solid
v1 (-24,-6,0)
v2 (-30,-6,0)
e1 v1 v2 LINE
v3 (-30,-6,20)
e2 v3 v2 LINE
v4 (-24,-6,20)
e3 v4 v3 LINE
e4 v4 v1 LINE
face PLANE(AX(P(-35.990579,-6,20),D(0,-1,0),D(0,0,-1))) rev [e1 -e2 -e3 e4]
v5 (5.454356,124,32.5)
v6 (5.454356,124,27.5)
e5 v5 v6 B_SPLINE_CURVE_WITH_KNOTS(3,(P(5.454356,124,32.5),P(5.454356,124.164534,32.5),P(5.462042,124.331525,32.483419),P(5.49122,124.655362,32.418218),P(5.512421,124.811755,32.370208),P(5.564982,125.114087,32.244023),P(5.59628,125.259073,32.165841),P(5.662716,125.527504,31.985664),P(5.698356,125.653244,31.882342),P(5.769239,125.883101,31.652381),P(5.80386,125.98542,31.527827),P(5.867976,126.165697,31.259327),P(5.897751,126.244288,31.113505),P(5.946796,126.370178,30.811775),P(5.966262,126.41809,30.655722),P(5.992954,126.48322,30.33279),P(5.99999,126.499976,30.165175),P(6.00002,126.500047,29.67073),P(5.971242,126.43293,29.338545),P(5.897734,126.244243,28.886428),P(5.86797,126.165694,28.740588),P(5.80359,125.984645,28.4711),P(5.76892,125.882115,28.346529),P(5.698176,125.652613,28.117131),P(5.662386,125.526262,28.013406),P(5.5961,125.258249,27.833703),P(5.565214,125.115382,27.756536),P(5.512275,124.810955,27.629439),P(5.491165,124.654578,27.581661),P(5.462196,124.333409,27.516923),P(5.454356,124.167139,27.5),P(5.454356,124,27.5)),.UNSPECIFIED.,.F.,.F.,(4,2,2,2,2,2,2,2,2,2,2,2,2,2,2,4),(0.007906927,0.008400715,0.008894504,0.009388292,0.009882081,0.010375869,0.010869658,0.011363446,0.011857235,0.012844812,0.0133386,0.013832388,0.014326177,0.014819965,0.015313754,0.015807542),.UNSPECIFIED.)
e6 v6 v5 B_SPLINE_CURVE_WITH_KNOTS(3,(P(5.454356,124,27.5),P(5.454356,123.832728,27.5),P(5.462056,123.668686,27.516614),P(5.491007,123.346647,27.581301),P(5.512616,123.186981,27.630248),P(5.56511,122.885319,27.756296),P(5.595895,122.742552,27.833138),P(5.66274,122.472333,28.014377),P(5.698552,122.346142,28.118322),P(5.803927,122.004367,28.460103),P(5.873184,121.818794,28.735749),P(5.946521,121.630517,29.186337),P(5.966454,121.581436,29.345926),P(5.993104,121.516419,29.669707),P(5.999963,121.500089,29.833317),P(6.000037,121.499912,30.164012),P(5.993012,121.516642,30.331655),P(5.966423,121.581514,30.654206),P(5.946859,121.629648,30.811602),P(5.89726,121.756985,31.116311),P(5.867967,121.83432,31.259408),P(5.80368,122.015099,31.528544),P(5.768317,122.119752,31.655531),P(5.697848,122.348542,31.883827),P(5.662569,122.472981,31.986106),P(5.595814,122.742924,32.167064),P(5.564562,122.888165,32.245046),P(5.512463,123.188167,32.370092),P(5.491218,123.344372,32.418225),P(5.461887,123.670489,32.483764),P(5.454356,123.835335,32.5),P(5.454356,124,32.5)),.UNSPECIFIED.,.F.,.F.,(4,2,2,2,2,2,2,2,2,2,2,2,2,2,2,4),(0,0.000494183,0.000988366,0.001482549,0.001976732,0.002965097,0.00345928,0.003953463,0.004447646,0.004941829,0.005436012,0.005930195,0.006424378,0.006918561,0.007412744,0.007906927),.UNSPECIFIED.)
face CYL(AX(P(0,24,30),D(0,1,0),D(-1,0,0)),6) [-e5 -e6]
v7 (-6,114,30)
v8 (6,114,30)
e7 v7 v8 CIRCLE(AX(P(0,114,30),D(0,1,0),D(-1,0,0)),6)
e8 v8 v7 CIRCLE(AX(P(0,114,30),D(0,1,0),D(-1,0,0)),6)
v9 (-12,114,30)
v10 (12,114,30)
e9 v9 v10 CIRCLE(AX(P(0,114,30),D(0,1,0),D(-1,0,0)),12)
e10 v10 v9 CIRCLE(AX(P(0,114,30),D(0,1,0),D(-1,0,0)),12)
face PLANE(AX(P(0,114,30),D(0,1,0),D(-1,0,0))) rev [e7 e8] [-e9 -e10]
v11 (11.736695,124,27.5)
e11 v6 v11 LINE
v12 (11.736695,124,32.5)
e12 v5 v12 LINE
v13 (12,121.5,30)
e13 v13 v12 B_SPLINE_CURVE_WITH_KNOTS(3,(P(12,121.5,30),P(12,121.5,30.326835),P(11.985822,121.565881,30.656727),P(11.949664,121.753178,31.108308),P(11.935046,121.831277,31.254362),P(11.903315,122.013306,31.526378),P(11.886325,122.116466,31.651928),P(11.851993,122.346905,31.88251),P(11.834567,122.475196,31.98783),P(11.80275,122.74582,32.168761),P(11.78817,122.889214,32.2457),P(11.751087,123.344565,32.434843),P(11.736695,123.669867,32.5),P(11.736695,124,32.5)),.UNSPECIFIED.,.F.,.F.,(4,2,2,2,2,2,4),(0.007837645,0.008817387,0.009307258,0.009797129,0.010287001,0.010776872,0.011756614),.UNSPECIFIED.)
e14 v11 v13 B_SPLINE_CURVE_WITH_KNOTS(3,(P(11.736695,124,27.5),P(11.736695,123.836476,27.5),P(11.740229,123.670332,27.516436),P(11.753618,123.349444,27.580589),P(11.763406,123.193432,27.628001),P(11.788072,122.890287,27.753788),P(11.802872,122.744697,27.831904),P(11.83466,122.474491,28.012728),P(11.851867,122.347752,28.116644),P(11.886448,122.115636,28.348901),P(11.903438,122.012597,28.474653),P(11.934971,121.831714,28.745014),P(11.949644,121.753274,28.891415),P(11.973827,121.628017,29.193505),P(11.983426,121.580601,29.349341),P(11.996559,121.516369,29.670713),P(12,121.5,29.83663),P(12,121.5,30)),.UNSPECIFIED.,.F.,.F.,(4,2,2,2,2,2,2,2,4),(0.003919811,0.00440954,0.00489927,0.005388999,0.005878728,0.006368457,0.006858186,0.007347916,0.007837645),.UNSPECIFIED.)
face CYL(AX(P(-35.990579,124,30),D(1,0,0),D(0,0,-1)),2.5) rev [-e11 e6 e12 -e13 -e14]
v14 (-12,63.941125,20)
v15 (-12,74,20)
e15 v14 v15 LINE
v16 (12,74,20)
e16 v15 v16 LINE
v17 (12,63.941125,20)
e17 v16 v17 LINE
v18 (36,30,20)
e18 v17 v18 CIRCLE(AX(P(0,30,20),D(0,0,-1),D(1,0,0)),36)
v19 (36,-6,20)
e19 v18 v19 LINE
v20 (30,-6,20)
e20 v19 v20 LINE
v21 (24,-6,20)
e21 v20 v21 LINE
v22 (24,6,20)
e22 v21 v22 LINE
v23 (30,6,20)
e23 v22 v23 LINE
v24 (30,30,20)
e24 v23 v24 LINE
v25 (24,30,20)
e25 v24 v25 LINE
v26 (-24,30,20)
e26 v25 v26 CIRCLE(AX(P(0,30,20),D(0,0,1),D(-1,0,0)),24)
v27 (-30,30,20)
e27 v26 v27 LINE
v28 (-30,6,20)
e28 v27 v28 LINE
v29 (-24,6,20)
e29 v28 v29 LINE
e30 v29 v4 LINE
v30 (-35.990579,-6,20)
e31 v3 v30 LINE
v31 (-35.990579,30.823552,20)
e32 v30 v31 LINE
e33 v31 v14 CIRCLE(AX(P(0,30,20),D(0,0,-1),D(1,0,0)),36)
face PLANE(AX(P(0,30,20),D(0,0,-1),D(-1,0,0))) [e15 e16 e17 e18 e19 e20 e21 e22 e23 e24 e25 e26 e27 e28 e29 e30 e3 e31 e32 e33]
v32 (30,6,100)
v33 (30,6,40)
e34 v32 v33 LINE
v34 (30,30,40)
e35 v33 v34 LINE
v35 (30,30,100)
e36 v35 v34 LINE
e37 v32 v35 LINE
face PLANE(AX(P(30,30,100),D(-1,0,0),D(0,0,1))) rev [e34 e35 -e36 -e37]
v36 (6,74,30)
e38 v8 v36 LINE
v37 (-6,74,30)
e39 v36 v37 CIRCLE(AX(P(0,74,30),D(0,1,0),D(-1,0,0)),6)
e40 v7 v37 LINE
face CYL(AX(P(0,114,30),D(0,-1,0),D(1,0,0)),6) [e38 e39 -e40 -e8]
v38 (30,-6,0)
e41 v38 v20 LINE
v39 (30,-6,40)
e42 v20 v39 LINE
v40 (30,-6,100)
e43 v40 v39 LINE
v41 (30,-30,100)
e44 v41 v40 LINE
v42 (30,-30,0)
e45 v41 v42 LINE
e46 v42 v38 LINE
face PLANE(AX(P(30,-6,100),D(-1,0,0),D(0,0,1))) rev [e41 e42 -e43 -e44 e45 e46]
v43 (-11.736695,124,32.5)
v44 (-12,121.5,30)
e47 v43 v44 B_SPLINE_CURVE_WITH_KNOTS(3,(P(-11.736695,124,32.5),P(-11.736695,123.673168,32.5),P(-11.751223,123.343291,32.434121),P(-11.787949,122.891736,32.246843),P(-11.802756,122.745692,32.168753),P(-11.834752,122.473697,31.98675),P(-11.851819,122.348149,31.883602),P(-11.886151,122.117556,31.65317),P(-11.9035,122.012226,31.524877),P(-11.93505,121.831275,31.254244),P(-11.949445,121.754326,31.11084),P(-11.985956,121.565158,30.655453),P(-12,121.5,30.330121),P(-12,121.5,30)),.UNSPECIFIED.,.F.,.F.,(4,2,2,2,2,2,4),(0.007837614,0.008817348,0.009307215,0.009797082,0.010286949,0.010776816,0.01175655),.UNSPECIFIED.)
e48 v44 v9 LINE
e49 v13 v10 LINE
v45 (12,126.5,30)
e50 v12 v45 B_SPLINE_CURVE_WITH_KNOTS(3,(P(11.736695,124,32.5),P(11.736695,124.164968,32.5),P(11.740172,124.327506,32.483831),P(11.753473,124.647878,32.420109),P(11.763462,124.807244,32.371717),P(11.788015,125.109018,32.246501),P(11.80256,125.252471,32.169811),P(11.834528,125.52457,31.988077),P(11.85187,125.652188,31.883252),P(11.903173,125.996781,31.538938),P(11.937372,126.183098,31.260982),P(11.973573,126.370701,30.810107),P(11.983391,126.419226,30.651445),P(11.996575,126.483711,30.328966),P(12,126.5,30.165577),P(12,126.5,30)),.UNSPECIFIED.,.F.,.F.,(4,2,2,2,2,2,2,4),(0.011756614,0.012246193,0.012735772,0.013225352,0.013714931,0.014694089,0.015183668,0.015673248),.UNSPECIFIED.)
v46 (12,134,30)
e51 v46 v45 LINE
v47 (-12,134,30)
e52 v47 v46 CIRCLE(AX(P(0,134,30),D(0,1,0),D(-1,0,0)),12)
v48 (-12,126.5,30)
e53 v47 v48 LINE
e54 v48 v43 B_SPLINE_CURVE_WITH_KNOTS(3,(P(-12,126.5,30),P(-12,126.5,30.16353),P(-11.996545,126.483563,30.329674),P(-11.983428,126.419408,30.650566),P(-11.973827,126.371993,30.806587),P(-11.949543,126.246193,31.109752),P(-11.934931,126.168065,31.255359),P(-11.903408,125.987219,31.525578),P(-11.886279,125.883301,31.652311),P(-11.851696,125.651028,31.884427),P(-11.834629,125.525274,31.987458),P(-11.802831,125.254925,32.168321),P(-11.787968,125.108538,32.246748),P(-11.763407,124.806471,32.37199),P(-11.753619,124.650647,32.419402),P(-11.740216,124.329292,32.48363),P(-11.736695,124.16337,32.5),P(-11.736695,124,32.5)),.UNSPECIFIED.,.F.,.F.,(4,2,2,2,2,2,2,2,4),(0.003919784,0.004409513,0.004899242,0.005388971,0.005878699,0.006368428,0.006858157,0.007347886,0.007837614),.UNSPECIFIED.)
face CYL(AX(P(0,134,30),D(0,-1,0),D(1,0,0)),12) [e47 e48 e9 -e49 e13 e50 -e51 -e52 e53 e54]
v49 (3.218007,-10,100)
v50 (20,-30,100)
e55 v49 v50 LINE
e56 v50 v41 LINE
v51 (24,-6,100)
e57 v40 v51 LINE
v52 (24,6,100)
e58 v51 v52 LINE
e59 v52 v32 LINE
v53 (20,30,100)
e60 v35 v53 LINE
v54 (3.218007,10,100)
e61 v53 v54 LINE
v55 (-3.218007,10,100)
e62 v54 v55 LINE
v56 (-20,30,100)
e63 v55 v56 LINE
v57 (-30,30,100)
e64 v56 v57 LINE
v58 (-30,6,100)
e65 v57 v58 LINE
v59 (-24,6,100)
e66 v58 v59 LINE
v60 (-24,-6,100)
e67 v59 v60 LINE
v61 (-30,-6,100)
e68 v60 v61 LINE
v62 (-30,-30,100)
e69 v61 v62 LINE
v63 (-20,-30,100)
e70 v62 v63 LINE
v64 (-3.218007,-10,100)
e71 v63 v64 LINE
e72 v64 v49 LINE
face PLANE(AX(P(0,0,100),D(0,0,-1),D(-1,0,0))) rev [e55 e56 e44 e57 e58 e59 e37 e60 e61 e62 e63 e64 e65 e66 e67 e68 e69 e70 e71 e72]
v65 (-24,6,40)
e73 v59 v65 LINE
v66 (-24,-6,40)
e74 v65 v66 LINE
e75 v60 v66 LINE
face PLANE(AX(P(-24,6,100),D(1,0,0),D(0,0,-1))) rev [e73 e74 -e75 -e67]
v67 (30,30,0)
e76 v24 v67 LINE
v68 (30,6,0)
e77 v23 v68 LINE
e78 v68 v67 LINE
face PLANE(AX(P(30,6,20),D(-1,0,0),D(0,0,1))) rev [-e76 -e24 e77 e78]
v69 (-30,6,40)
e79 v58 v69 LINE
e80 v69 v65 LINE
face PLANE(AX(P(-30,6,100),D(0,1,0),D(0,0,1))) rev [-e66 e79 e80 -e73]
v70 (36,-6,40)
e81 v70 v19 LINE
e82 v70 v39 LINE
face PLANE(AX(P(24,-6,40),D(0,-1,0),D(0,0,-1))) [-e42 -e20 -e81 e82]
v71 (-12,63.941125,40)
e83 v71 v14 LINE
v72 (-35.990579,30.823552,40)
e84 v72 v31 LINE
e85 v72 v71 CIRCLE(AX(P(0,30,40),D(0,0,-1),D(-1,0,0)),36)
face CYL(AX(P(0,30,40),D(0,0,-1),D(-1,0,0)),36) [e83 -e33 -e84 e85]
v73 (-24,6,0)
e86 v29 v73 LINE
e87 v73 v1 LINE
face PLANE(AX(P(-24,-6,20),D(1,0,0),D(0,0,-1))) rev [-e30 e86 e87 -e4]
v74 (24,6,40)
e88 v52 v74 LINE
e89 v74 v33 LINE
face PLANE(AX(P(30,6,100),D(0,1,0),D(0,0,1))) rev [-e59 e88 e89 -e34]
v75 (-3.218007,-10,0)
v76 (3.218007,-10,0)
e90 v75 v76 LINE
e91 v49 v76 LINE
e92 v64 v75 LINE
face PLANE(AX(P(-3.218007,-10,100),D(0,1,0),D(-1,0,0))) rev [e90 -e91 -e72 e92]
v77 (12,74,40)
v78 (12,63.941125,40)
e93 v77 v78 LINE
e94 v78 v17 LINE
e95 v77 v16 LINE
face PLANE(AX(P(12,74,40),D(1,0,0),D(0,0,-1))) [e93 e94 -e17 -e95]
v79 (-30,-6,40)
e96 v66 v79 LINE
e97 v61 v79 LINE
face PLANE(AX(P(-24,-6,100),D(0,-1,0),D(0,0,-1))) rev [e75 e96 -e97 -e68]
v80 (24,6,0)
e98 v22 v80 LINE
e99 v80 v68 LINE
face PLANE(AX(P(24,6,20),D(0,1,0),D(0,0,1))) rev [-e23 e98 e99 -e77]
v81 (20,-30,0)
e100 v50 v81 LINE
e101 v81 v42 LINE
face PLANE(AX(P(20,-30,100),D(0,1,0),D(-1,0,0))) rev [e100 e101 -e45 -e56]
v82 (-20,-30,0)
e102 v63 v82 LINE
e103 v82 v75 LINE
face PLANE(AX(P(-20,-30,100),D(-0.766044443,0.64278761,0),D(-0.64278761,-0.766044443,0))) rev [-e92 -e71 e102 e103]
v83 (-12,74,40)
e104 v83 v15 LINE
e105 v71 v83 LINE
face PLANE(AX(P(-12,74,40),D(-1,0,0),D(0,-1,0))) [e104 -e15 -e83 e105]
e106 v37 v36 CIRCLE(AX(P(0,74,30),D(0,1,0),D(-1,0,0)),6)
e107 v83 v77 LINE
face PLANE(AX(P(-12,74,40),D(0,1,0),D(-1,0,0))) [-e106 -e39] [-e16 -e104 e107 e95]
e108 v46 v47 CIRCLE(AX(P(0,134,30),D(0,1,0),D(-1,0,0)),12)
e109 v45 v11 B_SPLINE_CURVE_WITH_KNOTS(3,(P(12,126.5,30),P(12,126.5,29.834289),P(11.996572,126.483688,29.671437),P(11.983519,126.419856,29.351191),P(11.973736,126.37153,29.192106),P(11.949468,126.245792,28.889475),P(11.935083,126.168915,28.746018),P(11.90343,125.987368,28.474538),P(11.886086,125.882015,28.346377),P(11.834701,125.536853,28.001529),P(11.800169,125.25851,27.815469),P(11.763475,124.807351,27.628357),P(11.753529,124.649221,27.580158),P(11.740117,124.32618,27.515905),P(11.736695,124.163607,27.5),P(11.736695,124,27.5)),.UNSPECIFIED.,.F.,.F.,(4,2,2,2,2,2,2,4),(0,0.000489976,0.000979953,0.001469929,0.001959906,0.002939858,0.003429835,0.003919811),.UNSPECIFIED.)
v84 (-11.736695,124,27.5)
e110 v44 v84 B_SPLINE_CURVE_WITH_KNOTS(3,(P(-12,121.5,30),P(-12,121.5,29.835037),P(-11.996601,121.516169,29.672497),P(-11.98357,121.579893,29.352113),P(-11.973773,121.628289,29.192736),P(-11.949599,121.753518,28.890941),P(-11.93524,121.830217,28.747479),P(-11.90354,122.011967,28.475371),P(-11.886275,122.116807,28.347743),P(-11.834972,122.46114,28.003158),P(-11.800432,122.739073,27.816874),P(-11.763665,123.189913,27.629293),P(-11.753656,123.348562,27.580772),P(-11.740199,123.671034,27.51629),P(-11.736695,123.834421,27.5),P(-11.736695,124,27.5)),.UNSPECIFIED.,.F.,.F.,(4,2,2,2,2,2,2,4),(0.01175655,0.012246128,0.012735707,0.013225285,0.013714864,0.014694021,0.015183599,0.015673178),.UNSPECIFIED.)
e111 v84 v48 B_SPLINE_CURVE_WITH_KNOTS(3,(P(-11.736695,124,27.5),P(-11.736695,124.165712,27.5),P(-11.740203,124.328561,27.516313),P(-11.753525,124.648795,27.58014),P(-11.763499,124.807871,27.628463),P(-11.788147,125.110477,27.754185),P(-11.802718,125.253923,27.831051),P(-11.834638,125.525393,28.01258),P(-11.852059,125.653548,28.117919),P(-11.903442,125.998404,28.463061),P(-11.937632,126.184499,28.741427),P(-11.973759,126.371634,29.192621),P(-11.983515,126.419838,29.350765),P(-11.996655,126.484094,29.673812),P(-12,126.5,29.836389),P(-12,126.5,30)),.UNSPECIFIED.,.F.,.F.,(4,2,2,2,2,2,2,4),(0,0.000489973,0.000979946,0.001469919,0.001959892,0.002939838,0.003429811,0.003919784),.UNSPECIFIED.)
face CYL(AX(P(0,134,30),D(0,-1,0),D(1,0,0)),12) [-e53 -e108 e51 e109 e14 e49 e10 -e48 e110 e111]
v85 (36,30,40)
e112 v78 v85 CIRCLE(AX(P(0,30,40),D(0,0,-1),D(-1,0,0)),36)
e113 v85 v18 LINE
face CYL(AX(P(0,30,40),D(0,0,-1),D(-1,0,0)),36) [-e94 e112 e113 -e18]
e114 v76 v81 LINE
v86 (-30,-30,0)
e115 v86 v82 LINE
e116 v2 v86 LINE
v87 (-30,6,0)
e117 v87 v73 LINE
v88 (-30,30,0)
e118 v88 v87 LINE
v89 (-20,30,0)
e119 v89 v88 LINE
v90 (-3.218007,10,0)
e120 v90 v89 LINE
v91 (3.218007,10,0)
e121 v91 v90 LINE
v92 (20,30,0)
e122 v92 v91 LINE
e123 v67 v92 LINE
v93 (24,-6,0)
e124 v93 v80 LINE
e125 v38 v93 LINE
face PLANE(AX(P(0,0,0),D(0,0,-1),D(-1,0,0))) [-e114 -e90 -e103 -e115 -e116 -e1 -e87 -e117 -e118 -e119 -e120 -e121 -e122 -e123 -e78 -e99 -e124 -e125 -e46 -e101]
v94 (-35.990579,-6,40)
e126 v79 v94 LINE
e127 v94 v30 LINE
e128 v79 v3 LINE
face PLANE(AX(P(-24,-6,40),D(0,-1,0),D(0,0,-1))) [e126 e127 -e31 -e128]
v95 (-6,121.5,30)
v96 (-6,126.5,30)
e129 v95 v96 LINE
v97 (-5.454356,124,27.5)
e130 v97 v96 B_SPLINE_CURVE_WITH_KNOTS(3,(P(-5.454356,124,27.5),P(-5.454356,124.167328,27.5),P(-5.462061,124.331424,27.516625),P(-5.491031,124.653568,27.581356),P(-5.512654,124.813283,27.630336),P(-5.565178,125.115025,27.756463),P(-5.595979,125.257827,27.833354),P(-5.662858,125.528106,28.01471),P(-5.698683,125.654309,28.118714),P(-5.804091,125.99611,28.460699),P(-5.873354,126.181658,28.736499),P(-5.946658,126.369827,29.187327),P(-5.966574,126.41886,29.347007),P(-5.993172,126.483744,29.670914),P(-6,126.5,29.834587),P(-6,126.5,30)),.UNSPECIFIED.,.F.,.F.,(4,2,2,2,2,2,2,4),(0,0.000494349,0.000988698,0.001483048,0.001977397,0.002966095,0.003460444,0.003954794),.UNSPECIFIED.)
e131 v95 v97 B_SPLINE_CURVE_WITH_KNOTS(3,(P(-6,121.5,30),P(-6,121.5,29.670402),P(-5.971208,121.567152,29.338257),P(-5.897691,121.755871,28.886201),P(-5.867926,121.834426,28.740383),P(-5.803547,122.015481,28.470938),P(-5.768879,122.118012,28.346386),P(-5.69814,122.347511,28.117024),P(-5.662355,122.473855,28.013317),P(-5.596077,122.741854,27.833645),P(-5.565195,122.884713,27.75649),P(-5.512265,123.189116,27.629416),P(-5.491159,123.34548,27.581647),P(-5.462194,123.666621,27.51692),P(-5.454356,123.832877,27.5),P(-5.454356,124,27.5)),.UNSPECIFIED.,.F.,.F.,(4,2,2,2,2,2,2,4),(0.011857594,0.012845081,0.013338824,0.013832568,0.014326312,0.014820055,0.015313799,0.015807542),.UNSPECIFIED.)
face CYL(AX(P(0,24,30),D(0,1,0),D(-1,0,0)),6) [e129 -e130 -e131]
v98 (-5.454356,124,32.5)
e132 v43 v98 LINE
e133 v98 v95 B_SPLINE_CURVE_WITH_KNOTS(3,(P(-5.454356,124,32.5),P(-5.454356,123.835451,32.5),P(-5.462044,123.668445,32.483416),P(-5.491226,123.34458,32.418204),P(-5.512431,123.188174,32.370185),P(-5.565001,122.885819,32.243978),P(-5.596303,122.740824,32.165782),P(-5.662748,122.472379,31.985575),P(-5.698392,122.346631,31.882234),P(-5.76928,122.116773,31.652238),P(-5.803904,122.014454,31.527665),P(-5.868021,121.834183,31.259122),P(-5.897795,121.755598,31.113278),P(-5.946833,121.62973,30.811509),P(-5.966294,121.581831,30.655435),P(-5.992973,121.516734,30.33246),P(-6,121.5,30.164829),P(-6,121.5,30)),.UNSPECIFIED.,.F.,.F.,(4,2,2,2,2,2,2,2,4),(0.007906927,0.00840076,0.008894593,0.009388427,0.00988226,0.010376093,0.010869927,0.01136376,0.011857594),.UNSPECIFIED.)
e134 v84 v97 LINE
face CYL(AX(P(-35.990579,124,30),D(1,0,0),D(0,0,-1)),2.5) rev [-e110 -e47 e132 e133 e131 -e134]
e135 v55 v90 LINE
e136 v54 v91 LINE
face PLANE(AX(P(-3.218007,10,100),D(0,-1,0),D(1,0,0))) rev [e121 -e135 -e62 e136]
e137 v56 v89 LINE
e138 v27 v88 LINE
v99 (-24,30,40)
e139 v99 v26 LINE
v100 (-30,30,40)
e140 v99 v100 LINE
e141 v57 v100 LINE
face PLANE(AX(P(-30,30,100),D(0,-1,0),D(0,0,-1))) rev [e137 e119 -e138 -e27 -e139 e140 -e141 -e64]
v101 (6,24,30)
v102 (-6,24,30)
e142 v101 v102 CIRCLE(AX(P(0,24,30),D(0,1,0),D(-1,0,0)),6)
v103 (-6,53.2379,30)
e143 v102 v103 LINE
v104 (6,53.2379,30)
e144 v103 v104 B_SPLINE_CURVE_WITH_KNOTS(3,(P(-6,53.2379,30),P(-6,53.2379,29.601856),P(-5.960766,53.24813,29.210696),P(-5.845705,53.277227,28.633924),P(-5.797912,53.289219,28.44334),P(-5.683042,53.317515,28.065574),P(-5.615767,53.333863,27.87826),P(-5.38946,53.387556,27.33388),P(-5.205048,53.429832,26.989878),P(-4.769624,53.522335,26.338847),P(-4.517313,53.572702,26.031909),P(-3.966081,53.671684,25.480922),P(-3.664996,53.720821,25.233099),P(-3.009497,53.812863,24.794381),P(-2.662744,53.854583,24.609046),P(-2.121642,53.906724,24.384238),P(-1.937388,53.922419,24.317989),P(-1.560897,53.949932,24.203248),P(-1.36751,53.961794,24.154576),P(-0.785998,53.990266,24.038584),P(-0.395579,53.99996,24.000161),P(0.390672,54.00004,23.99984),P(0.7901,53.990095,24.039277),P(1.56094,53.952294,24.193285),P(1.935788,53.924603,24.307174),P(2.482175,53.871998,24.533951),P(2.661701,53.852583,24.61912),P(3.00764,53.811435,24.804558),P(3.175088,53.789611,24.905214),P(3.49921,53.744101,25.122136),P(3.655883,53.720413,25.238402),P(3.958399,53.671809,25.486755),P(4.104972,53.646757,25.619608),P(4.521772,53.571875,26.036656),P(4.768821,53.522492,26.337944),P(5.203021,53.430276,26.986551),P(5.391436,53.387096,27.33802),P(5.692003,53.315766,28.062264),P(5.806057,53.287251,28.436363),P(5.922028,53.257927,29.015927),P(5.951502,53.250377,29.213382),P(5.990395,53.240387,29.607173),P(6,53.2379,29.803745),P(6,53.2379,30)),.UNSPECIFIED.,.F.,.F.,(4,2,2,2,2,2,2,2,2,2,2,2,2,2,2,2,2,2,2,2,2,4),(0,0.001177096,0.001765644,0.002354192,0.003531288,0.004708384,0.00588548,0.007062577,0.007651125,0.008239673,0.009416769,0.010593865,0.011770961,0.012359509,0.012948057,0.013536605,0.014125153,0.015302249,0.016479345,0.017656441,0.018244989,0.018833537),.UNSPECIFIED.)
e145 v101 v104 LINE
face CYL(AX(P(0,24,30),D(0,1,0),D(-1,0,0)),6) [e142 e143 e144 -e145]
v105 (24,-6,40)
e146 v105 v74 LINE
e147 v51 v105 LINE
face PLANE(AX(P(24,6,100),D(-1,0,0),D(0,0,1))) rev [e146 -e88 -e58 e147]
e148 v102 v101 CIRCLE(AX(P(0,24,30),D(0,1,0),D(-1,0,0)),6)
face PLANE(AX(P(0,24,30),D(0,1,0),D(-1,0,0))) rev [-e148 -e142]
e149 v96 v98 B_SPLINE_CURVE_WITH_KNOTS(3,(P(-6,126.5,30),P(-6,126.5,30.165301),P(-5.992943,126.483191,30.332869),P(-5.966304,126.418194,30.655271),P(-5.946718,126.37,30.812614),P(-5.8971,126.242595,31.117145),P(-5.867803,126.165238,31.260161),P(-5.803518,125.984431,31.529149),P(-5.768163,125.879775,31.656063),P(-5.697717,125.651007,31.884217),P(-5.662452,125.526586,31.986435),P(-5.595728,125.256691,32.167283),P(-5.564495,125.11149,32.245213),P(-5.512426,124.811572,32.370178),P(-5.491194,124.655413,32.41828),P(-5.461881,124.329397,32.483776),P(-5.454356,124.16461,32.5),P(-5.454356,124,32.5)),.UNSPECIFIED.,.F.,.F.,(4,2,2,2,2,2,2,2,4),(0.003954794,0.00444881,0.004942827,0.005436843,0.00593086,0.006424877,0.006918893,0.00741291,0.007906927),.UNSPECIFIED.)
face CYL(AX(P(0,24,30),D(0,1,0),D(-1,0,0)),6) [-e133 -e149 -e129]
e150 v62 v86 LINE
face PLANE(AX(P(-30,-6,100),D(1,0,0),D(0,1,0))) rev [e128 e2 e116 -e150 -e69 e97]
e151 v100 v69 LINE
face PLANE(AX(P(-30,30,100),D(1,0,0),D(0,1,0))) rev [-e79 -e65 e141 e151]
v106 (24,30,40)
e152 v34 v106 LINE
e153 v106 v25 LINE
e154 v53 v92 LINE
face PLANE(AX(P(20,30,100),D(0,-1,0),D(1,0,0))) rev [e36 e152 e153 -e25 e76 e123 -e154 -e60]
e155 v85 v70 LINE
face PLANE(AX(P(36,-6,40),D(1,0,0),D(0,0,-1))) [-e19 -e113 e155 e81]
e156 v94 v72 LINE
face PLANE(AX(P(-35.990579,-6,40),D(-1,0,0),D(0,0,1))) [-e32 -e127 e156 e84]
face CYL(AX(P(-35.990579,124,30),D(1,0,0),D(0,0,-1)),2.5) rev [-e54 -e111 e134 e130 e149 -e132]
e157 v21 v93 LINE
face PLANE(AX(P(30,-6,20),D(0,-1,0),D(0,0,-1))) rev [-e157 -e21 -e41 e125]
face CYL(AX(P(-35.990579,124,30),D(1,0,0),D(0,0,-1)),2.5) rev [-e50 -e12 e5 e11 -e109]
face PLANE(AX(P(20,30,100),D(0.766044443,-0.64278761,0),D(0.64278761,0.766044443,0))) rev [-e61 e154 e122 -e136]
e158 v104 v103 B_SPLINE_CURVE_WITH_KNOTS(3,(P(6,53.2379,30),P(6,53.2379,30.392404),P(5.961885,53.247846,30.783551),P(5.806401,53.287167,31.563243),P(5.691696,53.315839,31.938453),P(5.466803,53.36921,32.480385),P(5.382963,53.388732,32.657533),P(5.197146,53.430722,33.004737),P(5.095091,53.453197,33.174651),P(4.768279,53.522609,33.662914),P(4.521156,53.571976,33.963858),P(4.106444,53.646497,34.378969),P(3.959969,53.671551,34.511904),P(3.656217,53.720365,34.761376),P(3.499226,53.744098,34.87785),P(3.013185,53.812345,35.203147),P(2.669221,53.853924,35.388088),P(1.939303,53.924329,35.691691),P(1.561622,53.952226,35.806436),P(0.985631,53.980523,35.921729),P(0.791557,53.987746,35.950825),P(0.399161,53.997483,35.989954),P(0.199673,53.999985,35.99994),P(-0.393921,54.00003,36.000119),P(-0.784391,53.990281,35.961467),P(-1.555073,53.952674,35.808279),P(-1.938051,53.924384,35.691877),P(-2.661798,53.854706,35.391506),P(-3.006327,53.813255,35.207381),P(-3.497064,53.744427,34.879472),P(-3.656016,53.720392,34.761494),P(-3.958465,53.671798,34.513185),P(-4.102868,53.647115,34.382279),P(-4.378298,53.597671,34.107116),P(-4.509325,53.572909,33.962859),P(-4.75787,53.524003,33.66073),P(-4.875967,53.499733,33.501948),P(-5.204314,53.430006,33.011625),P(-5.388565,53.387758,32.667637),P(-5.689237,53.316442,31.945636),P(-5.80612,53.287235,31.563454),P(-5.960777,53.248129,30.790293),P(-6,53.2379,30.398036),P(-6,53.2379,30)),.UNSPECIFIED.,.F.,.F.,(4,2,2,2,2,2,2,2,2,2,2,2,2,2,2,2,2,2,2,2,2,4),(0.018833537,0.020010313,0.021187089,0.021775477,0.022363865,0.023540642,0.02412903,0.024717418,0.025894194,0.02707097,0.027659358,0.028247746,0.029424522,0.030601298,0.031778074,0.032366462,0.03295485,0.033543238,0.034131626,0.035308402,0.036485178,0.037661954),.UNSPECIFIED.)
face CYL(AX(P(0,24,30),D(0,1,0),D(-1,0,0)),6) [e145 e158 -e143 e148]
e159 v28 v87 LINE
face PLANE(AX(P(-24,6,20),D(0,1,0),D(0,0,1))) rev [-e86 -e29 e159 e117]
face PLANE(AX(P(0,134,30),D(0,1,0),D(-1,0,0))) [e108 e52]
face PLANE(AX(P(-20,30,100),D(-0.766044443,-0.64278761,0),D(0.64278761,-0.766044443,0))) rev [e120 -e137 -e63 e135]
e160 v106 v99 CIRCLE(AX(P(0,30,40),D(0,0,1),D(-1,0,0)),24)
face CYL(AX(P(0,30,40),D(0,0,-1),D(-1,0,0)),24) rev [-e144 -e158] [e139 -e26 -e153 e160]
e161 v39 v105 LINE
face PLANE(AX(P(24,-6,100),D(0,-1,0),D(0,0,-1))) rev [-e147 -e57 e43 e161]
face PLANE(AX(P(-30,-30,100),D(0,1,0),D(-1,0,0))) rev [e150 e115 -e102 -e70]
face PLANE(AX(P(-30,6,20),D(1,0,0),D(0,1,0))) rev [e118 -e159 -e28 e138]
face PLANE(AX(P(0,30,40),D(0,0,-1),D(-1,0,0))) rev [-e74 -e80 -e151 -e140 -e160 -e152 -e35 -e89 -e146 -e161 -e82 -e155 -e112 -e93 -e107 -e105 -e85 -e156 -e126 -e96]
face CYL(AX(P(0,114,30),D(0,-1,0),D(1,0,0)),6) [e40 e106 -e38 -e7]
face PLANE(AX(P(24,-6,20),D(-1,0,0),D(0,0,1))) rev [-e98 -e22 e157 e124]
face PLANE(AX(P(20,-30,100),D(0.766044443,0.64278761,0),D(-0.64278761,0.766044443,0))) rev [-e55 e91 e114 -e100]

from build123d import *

# Parameters (mm, degrees)
V_BLOCK_BODY_DEPTH               = 100
CLAMP_YOKE_DEPTH                 = 40
YOKE_ARCH_CUT_DEPTH              = 20
CLAMP_SCREW_UPPER_SHANK_SKETCH_R = 6
CLAMP_SCREW_UPPER_SHANK_DEPTH    = 40
CLAMP_KNOB_SKETCH_R              = 12
CLAMP_KNOB_DEPTH                 = 20
KNOB_CROSS_HOLE_DEPTH            = 172.032160718
KNOB_CROSS_HOLE_DEPTH_BACK       = 172.032160718
KNOB_CROSS_HOLE_SKETCH_R         = 2.5
CLAMP_START                      = -110
CLAMP_SCREW_LOWER_SHANK_SKETCH_R = 6
CLAMP_SCREW_LOWER_SHANK_DEPTH    = 110


with BuildPart() as part:
    # V-Block Profile Sketch → V-Block Body (new body)
    with BuildSketch(Plane.XY):
        Polygon((-30, 30), (-20, 30), (-3.218007376, 10), (3.218007376, 10), (20, 30), (30, 30), (30, 6), (24, 6), (24, -6), (30, -6), (30, -30), (20, -30), (3.218007376, -10), (-3.218007376, -10), (-20, -30), (-30, -30), (-30, -6), (-24, -6), (-24, 6), (-30, 6), align=None)
    extrude(amount=V_BLOCK_BODY_DEPTH)

    # Clamp Yoke Sketch → Clamp Yoke (add)
    with BuildSketch(Plane(origin=(0, 0, 0), x_dir=(-1, 0, 0), z_dir=(0, 0, -1))):
        with BuildLine():
            Line((-24, -6), (-36, -6))
            Line((-36, -6), (-36, 30))
            ThreePointArc((-36, 30), (-29.393876913, 50.784609691), (-12, 63.941125497))
            Line((-12, 63.941125497), (-12, 74))
            Line((-12, 74), (12, 74))
            Line((12, 74), (12, 63.941125497))
            ThreePointArc((12, 63.941125497), (29.154199322, 51.11948536), (35.990578805, 30.823551635))
            Line((35.990578805, 30.823551635), (35.990578805, -6))
            Line((35.990578805, -6), (24, -6))
            Line((24, -6), (24, 6))
            Line((24, 6), (30, 6))
            Line((30, 6), (30, 30))
            Line((30, 30), (24, 30))
            ThreePointArc((24, 30), (0, 54), (-24, 30))
            Line((-24, 30), (-30, 30))
            Line((-30, 30), (-30, 6))
            Line((-30, 6), (-24, 6))
            Line((-24, 6), (-24, -6))
        make_face()
    extrude(amount=-CLAMP_YOKE_DEPTH)

    # Yoke Arch Cut Sketch → Yoke Arch Cut (cut)
    with BuildSketch(Plane(origin=(0, 0, 0), x_dir=(-1, 0, 0), z_dir=(0, 0, -1))):
        with BuildLine():
            Line((-30, -6), (-36, -6))
            Line((-36, -6), (-36, 30))
            ThreePointArc((-36, 30), (-29.393876913, 50.784609691), (-12, 63.941125497))
            Line((-12, 63.941125497), (-12, 74))
            Line((-12, 74), (12, 74))
            Line((12, 74), (12, 63.941125497))
            ThreePointArc((12, 63.941125497), (29.154199322, 51.11948536), (35.990578805, 30.823551635))
            Line((35.990578805, 30.823551635), (35.990578805, -6))
            Line((35.990578805, -6), (30, -6))
            Line((30, -6), (24, -6))
            Line((24, -6), (24, 6))
            Line((24, 6), (30, 6))
            Line((30, 6), (30, 30))
            Line((30, 30), (24, 30))
            ThreePointArc((24, 30), (0, 54), (-24, 30))
            Line((-24, 30), (-30, 30))
            Line((-30, 30), (-30, 6))
            Line((-30, 6), (-24, 6))
            Line((-24, 6), (-24, -6))
            Line((-24, -6), (-30, -6))
        make_face()
    extrude(amount=-YOKE_ARCH_CUT_DEPTH, mode=Mode.SUBTRACT)

    # Clamp Screw Upper Shank Sketch → Clamp Screw Upper Shank (add)
    with BuildSketch(Plane(origin=(0, 74, 0), x_dir=(1, 0, 0), z_dir=(0, 1, 0))):
        with Locations(Location((0, -30, 0), (0, 0, 180))):
            Circle(CLAMP_SCREW_UPPER_SHANK_SKETCH_R)
    extrude(amount=CLAMP_SCREW_UPPER_SHANK_DEPTH)

    # Clamp Knob Sketch → Clamp Knob (add)
    with BuildSketch(Plane(origin=(0, 114, 0), x_dir=(1, 0, 0), z_dir=(0, 1, 0))):
        with Locations(Location((0, -30, 0), (0, 0, 180))):
            Circle(CLAMP_KNOB_SKETCH_R)
    extrude(amount=CLAMP_KNOB_DEPTH)

    # Knob Cross Hole Sketch → Knob Cross Hole (cut, two sides: drawn at the far end of the back side and taken through both)
    with BuildSketch(Plane(origin=(0, 0, 0), x_dir=(0, 0, -1), z_dir=(1, 0, 0)).offset(-KNOB_CROSS_HOLE_DEPTH_BACK)):
        with Locations(Location((-30, 124, 0), (0, 0, 89.999999972))):
            Circle(KNOB_CROSS_HOLE_SKETCH_R)
    extrude(amount=KNOB_CROSS_HOLE_DEPTH + KNOB_CROSS_HOLE_DEPTH_BACK, mode=Mode.SUBTRACT)

    # Clamp Screw Lower Shank Sketch → Clamp Screw Lower Shank (add)
    with BuildSketch(Plane(origin=(0, 134, 0), x_dir=(1, 0, 0), z_dir=(0, 1, 0)).offset(CLAMP_START)):
        with Locations(Location((0, -30, 0), (0, 0, 180))):
            Circle(CLAMP_SCREW_LOWER_SHANK_SKETCH_R)
    extrude(amount=CLAMP_SCREW_LOWER_SHANK_DEPTH)


solid = part.part
